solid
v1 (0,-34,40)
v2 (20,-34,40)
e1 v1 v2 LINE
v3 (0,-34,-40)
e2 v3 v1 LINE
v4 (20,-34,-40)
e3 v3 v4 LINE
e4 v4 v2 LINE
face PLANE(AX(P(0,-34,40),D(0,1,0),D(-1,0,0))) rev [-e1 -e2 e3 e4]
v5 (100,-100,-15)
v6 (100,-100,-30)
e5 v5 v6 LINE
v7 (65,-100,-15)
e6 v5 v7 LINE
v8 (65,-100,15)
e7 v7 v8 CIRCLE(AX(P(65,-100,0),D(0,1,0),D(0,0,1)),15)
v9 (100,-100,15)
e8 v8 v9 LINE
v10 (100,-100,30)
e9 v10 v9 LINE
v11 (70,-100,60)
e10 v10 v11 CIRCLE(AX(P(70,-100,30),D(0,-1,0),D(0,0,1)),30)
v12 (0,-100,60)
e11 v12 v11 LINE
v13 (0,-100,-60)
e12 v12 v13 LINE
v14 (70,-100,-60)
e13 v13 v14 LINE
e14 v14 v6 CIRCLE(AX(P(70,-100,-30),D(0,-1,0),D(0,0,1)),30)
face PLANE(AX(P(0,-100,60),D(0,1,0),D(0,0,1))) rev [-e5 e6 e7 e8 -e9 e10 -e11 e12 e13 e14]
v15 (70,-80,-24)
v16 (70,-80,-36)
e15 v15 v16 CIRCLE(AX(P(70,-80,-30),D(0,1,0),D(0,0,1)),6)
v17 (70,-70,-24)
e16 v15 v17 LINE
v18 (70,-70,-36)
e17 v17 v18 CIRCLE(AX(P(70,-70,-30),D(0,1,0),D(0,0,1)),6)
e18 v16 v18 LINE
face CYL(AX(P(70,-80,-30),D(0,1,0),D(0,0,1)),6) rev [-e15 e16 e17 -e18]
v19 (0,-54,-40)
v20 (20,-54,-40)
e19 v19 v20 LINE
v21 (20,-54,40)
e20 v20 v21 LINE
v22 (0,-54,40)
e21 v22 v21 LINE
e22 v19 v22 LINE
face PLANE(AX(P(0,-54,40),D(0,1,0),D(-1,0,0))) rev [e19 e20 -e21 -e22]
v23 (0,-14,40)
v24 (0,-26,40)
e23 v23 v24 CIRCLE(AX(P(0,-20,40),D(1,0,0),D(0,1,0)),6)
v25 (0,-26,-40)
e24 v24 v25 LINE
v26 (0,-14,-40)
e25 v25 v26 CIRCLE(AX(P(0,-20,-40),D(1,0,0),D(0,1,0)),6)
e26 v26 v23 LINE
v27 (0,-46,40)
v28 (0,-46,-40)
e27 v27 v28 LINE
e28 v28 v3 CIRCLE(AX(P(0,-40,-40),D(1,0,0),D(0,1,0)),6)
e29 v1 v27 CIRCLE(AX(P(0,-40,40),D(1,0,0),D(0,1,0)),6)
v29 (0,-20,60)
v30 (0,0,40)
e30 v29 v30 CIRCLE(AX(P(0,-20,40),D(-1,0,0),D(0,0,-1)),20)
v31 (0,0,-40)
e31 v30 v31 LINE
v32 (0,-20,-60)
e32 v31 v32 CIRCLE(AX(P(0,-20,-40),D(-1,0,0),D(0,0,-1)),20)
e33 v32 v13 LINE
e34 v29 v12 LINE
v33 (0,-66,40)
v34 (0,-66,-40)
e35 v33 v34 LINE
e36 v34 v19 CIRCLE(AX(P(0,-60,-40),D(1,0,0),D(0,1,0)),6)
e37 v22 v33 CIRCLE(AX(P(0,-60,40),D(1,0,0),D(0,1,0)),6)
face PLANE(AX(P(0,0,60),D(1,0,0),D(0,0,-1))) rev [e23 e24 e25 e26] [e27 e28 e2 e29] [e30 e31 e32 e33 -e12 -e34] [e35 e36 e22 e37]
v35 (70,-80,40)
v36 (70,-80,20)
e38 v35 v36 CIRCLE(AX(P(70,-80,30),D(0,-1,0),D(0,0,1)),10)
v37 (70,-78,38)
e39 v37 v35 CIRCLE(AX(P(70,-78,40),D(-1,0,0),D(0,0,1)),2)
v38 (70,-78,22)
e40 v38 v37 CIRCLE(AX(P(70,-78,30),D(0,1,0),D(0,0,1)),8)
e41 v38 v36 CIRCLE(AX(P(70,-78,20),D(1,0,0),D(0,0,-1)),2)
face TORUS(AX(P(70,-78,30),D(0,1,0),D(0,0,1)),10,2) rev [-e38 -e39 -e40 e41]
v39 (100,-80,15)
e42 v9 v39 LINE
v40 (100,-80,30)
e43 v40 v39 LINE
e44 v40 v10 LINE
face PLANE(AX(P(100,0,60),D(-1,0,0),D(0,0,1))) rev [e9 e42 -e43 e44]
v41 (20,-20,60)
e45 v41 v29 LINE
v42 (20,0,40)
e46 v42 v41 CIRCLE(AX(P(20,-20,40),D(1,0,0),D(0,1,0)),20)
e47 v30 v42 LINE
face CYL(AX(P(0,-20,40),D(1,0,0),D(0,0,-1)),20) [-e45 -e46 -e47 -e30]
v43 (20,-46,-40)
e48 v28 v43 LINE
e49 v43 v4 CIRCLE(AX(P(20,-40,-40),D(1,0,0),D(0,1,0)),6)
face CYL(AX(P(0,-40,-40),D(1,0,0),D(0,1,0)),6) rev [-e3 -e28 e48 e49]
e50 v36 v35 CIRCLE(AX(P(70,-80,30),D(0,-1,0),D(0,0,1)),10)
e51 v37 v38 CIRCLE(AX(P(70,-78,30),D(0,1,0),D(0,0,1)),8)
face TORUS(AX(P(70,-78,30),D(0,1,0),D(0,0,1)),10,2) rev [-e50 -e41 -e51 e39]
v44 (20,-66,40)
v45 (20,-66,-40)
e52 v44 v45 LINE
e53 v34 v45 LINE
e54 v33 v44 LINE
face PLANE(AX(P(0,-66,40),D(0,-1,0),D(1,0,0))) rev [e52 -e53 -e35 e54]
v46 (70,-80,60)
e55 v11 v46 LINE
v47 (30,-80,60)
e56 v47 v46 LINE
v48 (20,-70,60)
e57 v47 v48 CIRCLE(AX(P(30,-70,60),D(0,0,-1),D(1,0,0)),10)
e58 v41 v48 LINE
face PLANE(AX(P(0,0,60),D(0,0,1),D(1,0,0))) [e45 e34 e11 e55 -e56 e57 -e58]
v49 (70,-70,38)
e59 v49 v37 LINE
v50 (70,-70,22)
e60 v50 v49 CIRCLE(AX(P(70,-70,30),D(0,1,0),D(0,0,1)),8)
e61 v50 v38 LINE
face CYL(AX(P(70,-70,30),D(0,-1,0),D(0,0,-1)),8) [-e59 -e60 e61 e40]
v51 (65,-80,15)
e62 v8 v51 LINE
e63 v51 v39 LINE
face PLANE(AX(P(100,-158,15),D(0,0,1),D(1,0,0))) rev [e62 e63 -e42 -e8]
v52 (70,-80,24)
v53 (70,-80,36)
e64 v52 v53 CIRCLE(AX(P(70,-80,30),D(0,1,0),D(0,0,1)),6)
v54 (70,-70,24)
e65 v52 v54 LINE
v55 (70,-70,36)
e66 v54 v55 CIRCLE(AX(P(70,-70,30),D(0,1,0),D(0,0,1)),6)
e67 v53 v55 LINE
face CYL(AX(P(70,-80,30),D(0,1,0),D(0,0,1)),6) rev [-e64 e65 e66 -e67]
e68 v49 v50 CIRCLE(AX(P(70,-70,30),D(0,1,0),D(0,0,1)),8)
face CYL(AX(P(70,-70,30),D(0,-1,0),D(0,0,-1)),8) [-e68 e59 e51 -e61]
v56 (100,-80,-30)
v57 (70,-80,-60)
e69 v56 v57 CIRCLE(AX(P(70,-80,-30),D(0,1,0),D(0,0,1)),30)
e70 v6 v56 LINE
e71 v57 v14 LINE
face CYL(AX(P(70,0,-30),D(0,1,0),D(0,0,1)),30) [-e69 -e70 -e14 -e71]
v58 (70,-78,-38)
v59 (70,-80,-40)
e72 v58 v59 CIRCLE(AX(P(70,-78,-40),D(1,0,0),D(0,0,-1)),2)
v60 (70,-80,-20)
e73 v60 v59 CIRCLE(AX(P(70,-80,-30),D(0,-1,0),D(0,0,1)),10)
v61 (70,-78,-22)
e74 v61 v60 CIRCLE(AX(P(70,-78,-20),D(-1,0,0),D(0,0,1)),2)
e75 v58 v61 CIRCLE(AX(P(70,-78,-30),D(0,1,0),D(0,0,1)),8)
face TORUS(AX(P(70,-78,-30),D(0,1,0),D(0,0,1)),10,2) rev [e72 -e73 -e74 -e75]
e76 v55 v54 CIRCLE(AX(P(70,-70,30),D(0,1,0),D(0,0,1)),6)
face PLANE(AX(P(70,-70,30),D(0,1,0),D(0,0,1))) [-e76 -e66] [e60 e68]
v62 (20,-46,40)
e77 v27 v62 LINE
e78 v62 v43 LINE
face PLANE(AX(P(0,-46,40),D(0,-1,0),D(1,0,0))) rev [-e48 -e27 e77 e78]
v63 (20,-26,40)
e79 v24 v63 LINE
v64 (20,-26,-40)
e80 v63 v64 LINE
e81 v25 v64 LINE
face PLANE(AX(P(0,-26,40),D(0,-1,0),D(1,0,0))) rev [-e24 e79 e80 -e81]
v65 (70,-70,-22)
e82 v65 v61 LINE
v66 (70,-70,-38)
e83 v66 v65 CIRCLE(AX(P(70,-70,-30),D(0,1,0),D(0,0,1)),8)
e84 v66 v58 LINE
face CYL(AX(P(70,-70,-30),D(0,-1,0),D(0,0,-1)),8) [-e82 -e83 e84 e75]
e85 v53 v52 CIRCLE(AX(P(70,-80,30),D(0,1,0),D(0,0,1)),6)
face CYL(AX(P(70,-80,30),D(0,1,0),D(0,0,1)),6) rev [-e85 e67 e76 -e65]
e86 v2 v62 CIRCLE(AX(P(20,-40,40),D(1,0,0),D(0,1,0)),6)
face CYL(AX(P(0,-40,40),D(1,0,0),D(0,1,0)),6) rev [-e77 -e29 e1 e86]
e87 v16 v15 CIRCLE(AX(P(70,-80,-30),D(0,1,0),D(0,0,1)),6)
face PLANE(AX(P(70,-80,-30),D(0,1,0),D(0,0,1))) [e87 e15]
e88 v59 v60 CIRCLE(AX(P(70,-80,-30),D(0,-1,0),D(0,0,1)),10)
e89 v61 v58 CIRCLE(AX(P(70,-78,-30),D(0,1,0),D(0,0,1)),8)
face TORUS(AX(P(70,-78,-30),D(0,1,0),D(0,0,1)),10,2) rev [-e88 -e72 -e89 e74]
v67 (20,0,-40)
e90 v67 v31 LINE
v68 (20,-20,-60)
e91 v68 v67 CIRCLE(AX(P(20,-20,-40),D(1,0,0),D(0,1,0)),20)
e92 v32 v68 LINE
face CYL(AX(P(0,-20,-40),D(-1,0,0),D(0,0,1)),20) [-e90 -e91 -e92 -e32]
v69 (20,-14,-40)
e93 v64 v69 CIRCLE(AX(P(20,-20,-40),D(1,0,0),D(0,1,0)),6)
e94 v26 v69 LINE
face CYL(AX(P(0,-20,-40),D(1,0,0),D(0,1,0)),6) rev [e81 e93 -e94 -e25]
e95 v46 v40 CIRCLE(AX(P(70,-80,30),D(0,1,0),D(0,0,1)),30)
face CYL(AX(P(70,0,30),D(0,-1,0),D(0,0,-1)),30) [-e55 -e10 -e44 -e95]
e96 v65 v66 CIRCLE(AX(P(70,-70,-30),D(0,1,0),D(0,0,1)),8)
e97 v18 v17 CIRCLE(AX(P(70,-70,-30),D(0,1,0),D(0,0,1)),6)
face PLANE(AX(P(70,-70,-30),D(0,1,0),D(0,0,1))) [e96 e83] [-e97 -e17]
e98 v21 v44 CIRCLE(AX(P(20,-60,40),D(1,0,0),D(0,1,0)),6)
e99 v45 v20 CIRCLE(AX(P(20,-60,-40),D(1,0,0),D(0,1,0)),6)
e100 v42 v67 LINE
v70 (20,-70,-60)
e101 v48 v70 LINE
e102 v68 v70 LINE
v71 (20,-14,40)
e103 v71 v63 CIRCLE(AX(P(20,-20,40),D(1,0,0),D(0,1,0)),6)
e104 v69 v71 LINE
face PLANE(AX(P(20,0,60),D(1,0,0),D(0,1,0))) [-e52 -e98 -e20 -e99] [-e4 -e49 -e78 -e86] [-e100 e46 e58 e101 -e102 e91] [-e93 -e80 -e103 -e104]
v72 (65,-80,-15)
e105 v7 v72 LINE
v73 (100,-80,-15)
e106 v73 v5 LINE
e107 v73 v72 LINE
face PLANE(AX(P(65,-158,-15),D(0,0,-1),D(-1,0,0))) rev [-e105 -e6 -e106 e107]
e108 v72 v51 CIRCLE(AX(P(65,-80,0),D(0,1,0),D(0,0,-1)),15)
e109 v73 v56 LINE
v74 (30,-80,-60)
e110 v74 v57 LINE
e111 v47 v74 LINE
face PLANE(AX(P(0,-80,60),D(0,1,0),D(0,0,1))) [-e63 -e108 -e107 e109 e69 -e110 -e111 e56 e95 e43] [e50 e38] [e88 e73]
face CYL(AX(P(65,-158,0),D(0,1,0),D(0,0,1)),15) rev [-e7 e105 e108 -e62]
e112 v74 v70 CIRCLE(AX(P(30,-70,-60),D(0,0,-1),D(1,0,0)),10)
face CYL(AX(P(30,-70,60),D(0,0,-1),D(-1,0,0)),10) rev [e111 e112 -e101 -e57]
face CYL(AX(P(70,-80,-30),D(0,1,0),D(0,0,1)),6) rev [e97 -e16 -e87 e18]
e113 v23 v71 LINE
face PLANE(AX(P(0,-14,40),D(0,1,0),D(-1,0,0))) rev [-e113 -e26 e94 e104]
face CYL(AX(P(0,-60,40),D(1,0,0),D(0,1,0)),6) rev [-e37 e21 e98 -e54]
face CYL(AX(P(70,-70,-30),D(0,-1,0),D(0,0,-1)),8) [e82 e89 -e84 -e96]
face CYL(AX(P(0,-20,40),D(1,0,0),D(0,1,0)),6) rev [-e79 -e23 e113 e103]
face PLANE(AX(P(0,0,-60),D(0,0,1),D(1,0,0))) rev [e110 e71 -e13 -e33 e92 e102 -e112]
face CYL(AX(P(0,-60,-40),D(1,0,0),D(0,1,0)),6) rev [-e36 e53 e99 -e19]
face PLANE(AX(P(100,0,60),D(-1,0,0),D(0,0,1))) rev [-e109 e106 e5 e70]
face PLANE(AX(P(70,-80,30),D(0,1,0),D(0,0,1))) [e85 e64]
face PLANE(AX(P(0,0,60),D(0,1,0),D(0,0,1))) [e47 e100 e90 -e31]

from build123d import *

# Parameters (mm, degrees)
BRACKET_BODY_DEPTH     = 60
CORNER_FILLET_R30_R    = 30
CORNER_FILLET_R20_R    = 20
BASE_NOTCH_DEPTH       = 78
UPRIGHT_SLOTS_3X_DEPTH = 20
BASE_BOSSES_PROFILE_R  = 8
BASE_BOSSES_2X_DEPTH   = 10
BOSS_EDGE_FILLET_R2_R  = 2
BOSS_HOLES_PROFILE_R   = 6
BOSS_HOLES_2X_DEPTH    = 10


with BuildPart() as part:
    # Bracket L Profile → Bracket Body (new, symmetric)
    with BuildSketch(Plane.XY):
        with BuildLine():
            Line((20, 0), (0, 0))
            Line((0, 0), (0, -80))
            Line((0, -80), (0, -100))
            Line((0, -100), (20, -100))
            Line((20, -100), (100, -100))
            Line((100, -100), (100, -80))
            Line((100, -80), (30, -80))
            ThreePointArc((30, -80), (22.928932188, -77.071067812), (20, -70))
            Line((20, -70), (20, 0))
        make_face()
    extrude(amount=BRACKET_BODY_DEPTH, both=True)

    # Corner Fillet R30
    corner_fillet_r30_edges = [part.edges().sort_by_distance(p)[0] for p in [
        (100, -90, 60),
        (100, -90, -60),
    ]]
    fillet(corner_fillet_r30_edges, radius=CORNER_FILLET_R30_R)

    # Corner Fillet R20
    corner_fillet_r20_edges = [part.edges().sort_by_distance(p)[0] for p in [
        (10, 0, -60),
        (10, 0, 60),
    ]]
    fillet(corner_fillet_r20_edges, radius=CORNER_FILLET_R20_R)

    # Base Notch Profile → Base Notch (cut)
    with BuildSketch(Plane(origin=(0, -80, 0), x_dir=(1, 0, 0), z_dir=(0, 1, 0))):
        with BuildLine():
            Line((65, 15), (100, 15))
            Line((100, 15), (100, -15))
            Line((100, -15), (65, -15))
            ThreePointArc((65, -15), (50, 0), (65, 15))
        make_face()
    extrude(amount=-BASE_NOTCH_DEPTH, mode=Mode.SUBTRACT)

    # Upright Slots Profile → Upright Slots 3x (cut)
    with BuildSketch(Plane(origin=(20, 0, 0), x_dir=(0, 0, -1), z_dir=(1, 0, 0))):
        with BuildLine():
            Line((-40, -14), (40, -14))
            ThreePointArc((40, -14), (46, -20), (40, -26))
            Line((40, -26), (-40, -26))
            ThreePointArc((-40, -26), (-46, -20), (-40, -14))
        make_face()
        with BuildLine():
            Line((-40, -46), (40, -46))
            ThreePointArc((40, -46), (46, -40), (40, -34))
            Line((40, -34), (-40, -34))
            ThreePointArc((-40, -34), (-46, -40), (-40, -46))
        make_face()
        with BuildLine():
            Line((-40, -66), (40, -66))
            ThreePointArc((40, -66), (46, -60), (40, -54))
            Line((40, -54), (-40, -54))
            ThreePointArc((-40, -54), (-46, -60), (-40, -66))
        make_face()
    extrude(amount=-UPRIGHT_SLOTS_3X_DEPTH, mode=Mode.SUBTRACT)

    # Base Bosses Profile → Base Bosses 2x (add)
    with BuildSketch(Plane(origin=(0, -80, 0), x_dir=(1, 0, 0), z_dir=(0, 1, 0))):
        with Locations(Location((70, 30, 0), (0, 0, 270))):
            Circle(BASE_BOSSES_PROFILE_R)
        with Locations(Location((70, -30, 0), (0, 0, 270))):
            Circle(BASE_BOSSES_PROFILE_R)
    extrude(amount=BASE_BOSSES_2X_DEPTH)

    # Boss Edge Fillet R2
    boss_edge_fillet_r2_edges = [part.edges().sort_by_distance(p)[0] for p in [
        (70, -80, -38),
        (70, -80, 22),
    ]]
    fillet(boss_edge_fillet_r2_edges, radius=BOSS_EDGE_FILLET_R2_R)

    # Boss Holes Profile → Boss Holes 2x (cut)
    with BuildSketch(Plane(origin=(0, -70, 0), x_dir=(1, 0, 0), z_dir=(0, 1, 0))):
        with Locations(Location((70, -30, 0), (0, 0, 270))):
            Circle(BOSS_HOLES_PROFILE_R)
        with Locations(Location((70, 30, 0), (0, 0, 270))):
            Circle(BOSS_HOLES_PROFILE_R)
    extrude(amount=-BOSS_HOLES_2X_DEPTH, mode=Mode.SUBTRACT)


solid = part.part
